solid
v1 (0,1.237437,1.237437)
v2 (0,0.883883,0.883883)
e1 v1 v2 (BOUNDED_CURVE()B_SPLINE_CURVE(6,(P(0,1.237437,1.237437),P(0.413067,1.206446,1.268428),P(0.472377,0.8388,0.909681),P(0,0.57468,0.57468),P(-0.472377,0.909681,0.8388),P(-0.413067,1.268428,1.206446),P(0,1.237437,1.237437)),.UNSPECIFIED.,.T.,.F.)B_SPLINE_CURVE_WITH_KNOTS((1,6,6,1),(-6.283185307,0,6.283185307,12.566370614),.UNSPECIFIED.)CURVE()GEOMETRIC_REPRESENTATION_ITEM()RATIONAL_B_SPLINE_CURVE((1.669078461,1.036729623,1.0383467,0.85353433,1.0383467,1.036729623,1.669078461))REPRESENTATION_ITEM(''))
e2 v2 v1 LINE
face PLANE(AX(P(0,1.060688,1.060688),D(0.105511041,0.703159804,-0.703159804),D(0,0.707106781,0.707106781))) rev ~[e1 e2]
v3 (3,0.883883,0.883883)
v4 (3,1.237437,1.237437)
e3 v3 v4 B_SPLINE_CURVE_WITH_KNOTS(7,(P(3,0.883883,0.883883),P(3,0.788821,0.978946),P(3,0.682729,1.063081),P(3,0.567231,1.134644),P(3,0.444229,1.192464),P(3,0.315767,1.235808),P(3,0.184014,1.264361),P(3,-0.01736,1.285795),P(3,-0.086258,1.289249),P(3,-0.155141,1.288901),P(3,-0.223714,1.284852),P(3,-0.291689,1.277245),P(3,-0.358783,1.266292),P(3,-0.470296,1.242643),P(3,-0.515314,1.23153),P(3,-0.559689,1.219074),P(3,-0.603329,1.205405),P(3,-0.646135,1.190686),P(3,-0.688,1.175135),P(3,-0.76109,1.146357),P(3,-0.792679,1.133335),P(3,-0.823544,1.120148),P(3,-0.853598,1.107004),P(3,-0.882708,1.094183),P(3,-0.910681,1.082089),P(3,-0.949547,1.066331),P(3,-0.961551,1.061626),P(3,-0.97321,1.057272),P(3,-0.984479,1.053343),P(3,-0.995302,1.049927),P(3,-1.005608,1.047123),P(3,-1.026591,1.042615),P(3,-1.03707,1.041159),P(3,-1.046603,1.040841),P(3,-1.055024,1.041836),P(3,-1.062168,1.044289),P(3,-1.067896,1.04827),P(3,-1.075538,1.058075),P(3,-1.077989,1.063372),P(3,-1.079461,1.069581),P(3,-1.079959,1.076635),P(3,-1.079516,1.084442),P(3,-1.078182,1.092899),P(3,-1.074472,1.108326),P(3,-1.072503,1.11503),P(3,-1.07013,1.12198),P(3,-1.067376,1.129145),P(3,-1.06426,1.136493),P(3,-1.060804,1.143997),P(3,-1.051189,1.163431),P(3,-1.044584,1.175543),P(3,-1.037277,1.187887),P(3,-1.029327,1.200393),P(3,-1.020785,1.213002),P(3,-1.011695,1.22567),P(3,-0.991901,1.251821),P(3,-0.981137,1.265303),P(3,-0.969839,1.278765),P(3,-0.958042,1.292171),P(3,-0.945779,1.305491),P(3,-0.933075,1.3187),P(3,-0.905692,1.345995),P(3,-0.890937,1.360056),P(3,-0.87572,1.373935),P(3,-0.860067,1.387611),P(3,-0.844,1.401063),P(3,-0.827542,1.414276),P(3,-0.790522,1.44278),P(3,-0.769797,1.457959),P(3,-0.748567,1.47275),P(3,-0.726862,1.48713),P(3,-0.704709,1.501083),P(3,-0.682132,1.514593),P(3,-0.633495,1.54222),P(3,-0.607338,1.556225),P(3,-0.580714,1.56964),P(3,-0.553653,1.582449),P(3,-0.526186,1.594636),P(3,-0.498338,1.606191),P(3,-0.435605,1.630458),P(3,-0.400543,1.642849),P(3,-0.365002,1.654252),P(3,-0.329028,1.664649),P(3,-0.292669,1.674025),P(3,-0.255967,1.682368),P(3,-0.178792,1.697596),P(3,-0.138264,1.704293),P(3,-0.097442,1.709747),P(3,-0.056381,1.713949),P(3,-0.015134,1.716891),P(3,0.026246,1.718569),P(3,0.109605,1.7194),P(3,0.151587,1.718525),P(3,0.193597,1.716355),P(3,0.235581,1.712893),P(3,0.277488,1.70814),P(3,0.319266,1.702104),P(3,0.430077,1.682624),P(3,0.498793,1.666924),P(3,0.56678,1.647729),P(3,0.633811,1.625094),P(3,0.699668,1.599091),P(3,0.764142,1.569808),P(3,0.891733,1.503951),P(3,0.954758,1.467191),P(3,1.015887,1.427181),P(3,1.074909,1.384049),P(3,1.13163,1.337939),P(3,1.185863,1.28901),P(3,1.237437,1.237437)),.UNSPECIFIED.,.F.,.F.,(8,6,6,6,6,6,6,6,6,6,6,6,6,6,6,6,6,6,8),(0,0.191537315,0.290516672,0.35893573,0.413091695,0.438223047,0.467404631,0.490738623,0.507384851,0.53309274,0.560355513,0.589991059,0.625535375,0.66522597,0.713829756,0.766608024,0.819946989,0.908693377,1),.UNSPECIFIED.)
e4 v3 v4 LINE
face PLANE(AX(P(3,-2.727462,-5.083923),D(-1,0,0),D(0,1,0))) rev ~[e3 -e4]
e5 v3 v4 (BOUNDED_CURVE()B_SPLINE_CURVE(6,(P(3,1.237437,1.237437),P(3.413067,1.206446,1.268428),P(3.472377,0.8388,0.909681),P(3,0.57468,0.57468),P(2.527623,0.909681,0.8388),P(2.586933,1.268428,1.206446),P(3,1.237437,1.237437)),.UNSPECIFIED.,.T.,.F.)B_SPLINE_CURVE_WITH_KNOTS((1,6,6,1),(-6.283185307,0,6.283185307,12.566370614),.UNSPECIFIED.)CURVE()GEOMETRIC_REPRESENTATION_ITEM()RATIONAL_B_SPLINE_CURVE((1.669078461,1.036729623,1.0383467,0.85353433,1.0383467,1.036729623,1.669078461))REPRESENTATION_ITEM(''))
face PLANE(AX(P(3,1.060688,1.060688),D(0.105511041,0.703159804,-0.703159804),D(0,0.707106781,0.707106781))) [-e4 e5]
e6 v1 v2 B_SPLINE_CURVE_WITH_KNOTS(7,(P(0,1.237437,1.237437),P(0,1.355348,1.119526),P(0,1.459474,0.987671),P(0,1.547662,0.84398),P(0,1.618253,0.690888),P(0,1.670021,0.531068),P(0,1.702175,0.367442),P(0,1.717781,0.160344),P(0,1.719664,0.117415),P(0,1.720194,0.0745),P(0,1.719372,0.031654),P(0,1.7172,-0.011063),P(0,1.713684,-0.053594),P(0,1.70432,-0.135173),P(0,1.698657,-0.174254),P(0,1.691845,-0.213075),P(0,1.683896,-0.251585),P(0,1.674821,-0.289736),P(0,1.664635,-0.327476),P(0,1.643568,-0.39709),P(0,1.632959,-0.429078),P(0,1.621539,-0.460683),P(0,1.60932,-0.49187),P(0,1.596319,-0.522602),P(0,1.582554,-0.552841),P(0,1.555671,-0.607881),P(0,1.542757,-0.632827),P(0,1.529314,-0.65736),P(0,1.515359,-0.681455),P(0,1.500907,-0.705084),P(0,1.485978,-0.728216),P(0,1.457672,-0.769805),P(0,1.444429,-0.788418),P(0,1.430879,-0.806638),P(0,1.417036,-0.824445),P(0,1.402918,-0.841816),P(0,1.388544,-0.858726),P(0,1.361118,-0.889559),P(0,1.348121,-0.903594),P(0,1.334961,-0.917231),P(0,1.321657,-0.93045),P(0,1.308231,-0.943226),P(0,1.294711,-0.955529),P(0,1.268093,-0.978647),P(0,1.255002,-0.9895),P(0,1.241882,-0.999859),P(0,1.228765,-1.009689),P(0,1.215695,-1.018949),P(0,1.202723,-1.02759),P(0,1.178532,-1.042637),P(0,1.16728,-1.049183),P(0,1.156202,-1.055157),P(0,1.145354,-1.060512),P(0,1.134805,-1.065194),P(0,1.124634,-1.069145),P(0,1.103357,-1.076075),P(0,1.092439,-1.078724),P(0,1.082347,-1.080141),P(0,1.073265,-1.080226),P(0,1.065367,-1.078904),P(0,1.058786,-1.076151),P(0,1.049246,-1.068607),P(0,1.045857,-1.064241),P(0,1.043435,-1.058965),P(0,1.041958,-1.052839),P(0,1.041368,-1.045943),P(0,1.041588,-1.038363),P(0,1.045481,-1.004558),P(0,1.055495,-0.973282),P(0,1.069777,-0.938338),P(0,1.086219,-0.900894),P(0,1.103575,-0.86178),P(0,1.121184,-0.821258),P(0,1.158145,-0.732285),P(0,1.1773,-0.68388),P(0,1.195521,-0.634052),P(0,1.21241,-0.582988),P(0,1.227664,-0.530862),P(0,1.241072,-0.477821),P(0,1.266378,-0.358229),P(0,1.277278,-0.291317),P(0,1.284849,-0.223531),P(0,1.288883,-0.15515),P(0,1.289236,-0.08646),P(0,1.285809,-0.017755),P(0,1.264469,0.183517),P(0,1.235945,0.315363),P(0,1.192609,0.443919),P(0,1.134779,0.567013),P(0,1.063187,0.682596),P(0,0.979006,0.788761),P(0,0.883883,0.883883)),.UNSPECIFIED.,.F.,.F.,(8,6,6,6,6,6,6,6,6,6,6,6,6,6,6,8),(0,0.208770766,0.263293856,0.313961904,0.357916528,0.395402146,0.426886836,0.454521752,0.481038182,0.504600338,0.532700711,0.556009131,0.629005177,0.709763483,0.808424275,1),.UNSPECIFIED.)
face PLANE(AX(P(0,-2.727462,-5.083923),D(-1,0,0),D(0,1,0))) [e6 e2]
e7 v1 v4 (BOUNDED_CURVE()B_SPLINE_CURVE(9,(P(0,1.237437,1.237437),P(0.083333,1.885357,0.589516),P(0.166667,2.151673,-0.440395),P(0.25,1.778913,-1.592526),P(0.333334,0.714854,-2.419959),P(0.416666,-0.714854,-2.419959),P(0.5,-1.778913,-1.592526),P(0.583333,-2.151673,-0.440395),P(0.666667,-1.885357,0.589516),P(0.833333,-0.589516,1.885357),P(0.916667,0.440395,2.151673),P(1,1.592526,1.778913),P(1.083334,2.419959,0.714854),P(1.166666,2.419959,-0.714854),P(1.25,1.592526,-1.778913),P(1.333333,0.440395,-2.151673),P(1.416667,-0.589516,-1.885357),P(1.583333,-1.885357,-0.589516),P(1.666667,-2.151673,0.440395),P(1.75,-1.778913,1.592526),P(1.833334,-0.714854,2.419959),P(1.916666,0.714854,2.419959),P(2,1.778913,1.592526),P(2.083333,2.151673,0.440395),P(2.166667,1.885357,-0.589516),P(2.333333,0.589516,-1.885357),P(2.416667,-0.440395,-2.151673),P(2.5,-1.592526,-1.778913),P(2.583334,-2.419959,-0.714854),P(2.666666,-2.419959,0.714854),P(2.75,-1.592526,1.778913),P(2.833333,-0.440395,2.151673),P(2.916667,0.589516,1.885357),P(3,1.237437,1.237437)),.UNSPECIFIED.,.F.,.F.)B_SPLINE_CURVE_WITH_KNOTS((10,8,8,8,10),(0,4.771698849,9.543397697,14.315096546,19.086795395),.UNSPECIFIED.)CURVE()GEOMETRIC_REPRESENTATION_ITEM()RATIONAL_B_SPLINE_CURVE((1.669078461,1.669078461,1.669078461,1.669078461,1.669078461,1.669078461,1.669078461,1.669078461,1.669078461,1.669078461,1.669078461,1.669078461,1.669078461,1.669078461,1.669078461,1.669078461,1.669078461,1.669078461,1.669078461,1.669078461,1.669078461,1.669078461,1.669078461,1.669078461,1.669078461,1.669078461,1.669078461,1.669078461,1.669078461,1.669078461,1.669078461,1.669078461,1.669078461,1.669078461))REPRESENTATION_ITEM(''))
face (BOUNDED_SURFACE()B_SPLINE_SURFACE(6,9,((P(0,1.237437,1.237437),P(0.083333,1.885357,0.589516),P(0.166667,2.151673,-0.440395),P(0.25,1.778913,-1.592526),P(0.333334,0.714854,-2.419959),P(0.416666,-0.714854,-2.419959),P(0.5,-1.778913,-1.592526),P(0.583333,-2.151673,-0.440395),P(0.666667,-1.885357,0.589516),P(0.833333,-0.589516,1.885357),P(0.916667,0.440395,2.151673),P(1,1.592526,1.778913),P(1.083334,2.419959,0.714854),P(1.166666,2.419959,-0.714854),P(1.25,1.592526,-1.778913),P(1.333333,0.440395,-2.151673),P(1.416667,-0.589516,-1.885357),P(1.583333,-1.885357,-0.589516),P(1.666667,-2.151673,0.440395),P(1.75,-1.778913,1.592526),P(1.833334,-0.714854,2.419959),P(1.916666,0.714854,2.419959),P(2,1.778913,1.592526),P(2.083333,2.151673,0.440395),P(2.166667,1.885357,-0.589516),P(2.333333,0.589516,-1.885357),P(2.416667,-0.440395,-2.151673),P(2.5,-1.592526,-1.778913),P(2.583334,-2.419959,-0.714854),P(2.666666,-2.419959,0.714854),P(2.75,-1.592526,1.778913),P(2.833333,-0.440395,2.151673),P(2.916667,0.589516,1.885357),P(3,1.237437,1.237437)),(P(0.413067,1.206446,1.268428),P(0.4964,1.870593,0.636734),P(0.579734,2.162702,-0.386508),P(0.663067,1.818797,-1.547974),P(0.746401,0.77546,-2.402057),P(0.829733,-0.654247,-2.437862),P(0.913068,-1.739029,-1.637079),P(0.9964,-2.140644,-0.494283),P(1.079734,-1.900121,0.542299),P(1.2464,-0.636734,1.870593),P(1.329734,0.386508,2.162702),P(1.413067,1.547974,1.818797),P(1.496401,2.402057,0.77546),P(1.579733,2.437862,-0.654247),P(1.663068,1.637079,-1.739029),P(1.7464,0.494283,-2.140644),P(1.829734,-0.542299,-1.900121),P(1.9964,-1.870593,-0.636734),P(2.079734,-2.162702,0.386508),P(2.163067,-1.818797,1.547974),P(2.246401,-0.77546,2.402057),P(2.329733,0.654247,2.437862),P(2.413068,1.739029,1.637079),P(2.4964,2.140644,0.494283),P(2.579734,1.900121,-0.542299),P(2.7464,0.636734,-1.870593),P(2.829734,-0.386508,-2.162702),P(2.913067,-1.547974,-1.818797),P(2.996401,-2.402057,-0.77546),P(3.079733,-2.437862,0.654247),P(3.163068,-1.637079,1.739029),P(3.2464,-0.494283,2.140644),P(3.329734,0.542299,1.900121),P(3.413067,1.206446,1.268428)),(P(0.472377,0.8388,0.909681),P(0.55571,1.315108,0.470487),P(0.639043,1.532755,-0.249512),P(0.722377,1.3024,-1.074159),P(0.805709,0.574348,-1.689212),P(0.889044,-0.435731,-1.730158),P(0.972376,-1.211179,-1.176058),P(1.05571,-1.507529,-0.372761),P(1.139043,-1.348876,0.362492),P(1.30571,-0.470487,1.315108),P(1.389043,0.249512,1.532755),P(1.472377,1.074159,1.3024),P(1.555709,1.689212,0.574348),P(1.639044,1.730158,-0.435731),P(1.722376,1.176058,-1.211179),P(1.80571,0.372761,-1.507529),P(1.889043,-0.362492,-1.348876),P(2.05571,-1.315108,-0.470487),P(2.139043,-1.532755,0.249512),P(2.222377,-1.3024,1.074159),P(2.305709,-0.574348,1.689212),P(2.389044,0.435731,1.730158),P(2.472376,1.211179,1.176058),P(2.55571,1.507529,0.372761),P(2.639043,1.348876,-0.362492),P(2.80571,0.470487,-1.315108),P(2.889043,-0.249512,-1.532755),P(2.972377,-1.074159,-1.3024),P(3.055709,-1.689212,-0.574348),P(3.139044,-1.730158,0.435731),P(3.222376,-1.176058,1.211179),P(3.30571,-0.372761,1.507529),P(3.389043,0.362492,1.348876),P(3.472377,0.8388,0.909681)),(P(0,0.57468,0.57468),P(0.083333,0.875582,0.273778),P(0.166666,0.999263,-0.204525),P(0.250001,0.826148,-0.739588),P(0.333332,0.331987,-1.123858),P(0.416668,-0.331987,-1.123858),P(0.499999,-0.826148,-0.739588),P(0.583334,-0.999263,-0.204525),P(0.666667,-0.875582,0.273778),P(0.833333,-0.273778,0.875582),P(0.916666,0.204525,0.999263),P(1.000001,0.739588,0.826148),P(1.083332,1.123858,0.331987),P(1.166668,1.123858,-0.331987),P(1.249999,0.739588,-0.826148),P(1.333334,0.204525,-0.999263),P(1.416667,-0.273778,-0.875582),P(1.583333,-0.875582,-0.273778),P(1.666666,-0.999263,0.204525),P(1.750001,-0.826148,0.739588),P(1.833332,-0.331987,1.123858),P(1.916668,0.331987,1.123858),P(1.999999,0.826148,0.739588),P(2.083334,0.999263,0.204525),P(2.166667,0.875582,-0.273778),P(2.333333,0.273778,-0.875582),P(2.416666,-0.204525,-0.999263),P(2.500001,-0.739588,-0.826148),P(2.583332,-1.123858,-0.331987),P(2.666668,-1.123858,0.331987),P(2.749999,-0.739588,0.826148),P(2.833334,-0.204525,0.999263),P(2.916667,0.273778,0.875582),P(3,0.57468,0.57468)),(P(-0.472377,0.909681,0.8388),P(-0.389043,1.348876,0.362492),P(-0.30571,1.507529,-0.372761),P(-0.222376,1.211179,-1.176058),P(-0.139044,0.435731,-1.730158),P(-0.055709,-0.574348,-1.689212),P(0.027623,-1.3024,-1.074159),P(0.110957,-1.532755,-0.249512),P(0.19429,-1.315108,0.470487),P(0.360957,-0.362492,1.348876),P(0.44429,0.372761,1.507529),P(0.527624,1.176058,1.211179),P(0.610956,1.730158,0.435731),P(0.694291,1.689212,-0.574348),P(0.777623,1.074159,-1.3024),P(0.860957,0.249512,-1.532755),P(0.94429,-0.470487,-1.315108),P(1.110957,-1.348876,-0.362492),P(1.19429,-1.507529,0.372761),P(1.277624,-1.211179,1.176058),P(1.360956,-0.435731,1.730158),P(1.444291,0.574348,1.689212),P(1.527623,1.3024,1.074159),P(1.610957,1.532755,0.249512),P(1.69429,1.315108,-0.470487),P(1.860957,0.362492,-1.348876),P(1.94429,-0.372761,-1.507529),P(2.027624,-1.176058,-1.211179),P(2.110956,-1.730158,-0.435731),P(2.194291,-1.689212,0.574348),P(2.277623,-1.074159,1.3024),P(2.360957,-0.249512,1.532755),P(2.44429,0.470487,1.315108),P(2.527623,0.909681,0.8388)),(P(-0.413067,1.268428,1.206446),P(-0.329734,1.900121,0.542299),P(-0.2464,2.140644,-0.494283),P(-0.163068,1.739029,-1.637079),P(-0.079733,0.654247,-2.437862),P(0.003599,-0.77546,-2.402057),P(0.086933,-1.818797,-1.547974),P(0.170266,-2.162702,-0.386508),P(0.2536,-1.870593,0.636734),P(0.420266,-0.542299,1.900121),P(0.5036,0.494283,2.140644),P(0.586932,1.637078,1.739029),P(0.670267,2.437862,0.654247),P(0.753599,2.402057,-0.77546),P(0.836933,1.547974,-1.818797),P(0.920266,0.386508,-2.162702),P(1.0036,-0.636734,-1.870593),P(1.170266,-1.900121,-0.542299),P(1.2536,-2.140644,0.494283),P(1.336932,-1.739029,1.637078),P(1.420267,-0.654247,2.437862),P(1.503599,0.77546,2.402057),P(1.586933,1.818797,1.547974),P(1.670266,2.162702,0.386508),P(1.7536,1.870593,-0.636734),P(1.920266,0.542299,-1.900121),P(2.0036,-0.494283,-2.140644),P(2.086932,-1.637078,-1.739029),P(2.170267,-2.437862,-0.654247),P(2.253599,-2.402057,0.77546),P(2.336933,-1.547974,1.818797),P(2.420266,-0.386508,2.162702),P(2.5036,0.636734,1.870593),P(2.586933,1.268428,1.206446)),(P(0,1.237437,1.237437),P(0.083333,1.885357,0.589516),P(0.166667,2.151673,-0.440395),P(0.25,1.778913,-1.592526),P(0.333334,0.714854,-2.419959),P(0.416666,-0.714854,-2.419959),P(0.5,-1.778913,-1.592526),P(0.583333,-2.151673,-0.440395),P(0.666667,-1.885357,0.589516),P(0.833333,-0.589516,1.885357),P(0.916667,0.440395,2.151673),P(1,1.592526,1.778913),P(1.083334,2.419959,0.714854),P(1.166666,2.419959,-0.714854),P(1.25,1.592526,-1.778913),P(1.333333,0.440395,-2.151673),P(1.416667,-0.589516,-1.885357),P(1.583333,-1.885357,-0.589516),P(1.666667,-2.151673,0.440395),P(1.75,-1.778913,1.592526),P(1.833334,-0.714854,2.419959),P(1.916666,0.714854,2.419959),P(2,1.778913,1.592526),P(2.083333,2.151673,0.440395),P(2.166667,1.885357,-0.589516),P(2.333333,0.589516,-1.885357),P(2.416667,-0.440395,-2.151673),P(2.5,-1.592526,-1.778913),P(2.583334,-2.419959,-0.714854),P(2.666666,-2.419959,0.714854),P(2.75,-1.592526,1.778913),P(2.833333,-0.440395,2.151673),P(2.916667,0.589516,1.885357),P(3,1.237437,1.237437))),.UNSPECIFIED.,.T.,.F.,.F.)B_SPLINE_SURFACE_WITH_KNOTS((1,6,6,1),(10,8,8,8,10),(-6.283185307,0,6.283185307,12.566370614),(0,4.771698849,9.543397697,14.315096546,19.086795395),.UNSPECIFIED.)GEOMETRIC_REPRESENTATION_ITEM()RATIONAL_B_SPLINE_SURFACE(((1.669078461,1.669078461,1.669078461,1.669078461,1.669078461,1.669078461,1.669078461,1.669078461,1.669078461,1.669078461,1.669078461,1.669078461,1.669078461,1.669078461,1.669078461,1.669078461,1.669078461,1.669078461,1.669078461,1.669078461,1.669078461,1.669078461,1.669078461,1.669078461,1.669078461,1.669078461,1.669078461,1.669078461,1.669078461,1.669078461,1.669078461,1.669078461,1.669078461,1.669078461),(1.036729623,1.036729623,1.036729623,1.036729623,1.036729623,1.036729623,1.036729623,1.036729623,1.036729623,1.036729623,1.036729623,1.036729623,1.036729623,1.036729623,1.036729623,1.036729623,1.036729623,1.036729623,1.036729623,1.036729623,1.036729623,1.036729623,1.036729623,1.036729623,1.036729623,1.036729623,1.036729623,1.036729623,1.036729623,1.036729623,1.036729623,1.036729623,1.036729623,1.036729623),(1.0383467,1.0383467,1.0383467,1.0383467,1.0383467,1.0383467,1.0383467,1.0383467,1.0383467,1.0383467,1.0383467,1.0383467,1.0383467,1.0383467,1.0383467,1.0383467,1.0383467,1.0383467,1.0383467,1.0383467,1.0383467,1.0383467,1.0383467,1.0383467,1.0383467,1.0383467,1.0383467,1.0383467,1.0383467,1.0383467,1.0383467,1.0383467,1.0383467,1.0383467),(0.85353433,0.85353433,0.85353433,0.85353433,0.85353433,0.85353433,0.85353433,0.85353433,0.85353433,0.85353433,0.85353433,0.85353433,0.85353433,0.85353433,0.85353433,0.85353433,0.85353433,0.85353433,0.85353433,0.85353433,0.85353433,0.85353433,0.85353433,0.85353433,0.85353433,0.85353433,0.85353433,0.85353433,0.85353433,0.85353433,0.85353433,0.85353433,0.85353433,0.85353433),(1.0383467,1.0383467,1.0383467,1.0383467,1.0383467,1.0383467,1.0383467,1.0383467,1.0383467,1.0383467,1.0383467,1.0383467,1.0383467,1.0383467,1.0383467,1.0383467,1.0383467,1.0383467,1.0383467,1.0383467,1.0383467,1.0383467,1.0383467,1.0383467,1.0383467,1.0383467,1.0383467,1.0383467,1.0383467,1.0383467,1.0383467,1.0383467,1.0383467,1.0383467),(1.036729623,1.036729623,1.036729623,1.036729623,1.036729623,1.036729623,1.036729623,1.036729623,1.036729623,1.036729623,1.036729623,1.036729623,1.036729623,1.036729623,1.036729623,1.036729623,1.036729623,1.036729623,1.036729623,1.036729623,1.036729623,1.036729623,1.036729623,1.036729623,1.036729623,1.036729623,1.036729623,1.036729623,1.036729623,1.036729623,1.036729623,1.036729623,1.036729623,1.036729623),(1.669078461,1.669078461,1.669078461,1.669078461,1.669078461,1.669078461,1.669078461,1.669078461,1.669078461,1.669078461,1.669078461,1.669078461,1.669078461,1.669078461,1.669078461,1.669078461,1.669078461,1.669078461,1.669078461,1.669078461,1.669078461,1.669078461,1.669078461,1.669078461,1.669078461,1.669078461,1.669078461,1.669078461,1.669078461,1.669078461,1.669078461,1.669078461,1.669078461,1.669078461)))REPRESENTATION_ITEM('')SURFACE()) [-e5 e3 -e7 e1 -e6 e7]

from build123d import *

# Parameters (mm, degrees)
SWEEP1_PITCH            = 1
SWEEP1_HEIGHT           = 3
SWEEP1_RADIUS           = 1.5
SWEEP1_START_ANGLE      = -45
SWEEP1_PROFILE_R        = 0.25
CUT_EXTRUDE2_DEPTH      = 5.083922994
CUT_EXTRUDE2_DEPTH_BACK = 5.083922994
SKETCH8_OUTSIDE_W       = 6.71
SKETCH8_OUTSIDE_H       = 6.712
SKETCH8_OUTSIDE_W_2     = 3
SKETCH8_OUTSIDE_H_2     = 5.007784657


with BuildPart() as part:
    # Sweep1: sweep along a helix
    with BuildLine() as sweep1_path:
        add(Helix(SWEEP1_PITCH, SWEEP1_HEIGHT, SWEEP1_RADIUS, center=(0, 0, 0), direction=(1, 0, 0), lefthand=True, mode=Mode.PRIVATE).rotate(Axis((0, 0, 0), (1, 0, 0)), SWEEP1_START_ANGLE))
    # Sweep1 profile (on start of the path) → Sweep1 (sweep)
    with BuildSketch(Plane(origin=(0, 1.060660172, 1.060660172), x_dir=(0, 0.7071067811865146, 0.7071067811865807), z_dir=(0.1055110407535529, 0.7031598041267698, -0.7031598041267042))):
        Circle(SWEEP1_PROFILE_R)
    sweep(path=sweep1_path.line, is_frenet=True)

    # Sketch8 outside → Cut-Extrude2 (cut, two sides: drawn at the far end of the back side and taken through both)
    with BuildSketch(Plane.XY.offset(-CUT_EXTRUDE2_DEPTH_BACK)):
        with Locations((1.5, 0)):
            Rectangle(SKETCH8_OUTSIDE_W, SKETCH8_OUTSIDE_H)
        with Locations((1.5, -0.22356974)):
            Rectangle(SKETCH8_OUTSIDE_W_2, SKETCH8_OUTSIDE_H_2, mode=Mode.SUBTRACT)
    extrude(amount=CUT_EXTRUDE2_DEPTH + CUT_EXTRUDE2_DEPTH_BACK, mode=Mode.SUBTRACT)


solid = part.part
